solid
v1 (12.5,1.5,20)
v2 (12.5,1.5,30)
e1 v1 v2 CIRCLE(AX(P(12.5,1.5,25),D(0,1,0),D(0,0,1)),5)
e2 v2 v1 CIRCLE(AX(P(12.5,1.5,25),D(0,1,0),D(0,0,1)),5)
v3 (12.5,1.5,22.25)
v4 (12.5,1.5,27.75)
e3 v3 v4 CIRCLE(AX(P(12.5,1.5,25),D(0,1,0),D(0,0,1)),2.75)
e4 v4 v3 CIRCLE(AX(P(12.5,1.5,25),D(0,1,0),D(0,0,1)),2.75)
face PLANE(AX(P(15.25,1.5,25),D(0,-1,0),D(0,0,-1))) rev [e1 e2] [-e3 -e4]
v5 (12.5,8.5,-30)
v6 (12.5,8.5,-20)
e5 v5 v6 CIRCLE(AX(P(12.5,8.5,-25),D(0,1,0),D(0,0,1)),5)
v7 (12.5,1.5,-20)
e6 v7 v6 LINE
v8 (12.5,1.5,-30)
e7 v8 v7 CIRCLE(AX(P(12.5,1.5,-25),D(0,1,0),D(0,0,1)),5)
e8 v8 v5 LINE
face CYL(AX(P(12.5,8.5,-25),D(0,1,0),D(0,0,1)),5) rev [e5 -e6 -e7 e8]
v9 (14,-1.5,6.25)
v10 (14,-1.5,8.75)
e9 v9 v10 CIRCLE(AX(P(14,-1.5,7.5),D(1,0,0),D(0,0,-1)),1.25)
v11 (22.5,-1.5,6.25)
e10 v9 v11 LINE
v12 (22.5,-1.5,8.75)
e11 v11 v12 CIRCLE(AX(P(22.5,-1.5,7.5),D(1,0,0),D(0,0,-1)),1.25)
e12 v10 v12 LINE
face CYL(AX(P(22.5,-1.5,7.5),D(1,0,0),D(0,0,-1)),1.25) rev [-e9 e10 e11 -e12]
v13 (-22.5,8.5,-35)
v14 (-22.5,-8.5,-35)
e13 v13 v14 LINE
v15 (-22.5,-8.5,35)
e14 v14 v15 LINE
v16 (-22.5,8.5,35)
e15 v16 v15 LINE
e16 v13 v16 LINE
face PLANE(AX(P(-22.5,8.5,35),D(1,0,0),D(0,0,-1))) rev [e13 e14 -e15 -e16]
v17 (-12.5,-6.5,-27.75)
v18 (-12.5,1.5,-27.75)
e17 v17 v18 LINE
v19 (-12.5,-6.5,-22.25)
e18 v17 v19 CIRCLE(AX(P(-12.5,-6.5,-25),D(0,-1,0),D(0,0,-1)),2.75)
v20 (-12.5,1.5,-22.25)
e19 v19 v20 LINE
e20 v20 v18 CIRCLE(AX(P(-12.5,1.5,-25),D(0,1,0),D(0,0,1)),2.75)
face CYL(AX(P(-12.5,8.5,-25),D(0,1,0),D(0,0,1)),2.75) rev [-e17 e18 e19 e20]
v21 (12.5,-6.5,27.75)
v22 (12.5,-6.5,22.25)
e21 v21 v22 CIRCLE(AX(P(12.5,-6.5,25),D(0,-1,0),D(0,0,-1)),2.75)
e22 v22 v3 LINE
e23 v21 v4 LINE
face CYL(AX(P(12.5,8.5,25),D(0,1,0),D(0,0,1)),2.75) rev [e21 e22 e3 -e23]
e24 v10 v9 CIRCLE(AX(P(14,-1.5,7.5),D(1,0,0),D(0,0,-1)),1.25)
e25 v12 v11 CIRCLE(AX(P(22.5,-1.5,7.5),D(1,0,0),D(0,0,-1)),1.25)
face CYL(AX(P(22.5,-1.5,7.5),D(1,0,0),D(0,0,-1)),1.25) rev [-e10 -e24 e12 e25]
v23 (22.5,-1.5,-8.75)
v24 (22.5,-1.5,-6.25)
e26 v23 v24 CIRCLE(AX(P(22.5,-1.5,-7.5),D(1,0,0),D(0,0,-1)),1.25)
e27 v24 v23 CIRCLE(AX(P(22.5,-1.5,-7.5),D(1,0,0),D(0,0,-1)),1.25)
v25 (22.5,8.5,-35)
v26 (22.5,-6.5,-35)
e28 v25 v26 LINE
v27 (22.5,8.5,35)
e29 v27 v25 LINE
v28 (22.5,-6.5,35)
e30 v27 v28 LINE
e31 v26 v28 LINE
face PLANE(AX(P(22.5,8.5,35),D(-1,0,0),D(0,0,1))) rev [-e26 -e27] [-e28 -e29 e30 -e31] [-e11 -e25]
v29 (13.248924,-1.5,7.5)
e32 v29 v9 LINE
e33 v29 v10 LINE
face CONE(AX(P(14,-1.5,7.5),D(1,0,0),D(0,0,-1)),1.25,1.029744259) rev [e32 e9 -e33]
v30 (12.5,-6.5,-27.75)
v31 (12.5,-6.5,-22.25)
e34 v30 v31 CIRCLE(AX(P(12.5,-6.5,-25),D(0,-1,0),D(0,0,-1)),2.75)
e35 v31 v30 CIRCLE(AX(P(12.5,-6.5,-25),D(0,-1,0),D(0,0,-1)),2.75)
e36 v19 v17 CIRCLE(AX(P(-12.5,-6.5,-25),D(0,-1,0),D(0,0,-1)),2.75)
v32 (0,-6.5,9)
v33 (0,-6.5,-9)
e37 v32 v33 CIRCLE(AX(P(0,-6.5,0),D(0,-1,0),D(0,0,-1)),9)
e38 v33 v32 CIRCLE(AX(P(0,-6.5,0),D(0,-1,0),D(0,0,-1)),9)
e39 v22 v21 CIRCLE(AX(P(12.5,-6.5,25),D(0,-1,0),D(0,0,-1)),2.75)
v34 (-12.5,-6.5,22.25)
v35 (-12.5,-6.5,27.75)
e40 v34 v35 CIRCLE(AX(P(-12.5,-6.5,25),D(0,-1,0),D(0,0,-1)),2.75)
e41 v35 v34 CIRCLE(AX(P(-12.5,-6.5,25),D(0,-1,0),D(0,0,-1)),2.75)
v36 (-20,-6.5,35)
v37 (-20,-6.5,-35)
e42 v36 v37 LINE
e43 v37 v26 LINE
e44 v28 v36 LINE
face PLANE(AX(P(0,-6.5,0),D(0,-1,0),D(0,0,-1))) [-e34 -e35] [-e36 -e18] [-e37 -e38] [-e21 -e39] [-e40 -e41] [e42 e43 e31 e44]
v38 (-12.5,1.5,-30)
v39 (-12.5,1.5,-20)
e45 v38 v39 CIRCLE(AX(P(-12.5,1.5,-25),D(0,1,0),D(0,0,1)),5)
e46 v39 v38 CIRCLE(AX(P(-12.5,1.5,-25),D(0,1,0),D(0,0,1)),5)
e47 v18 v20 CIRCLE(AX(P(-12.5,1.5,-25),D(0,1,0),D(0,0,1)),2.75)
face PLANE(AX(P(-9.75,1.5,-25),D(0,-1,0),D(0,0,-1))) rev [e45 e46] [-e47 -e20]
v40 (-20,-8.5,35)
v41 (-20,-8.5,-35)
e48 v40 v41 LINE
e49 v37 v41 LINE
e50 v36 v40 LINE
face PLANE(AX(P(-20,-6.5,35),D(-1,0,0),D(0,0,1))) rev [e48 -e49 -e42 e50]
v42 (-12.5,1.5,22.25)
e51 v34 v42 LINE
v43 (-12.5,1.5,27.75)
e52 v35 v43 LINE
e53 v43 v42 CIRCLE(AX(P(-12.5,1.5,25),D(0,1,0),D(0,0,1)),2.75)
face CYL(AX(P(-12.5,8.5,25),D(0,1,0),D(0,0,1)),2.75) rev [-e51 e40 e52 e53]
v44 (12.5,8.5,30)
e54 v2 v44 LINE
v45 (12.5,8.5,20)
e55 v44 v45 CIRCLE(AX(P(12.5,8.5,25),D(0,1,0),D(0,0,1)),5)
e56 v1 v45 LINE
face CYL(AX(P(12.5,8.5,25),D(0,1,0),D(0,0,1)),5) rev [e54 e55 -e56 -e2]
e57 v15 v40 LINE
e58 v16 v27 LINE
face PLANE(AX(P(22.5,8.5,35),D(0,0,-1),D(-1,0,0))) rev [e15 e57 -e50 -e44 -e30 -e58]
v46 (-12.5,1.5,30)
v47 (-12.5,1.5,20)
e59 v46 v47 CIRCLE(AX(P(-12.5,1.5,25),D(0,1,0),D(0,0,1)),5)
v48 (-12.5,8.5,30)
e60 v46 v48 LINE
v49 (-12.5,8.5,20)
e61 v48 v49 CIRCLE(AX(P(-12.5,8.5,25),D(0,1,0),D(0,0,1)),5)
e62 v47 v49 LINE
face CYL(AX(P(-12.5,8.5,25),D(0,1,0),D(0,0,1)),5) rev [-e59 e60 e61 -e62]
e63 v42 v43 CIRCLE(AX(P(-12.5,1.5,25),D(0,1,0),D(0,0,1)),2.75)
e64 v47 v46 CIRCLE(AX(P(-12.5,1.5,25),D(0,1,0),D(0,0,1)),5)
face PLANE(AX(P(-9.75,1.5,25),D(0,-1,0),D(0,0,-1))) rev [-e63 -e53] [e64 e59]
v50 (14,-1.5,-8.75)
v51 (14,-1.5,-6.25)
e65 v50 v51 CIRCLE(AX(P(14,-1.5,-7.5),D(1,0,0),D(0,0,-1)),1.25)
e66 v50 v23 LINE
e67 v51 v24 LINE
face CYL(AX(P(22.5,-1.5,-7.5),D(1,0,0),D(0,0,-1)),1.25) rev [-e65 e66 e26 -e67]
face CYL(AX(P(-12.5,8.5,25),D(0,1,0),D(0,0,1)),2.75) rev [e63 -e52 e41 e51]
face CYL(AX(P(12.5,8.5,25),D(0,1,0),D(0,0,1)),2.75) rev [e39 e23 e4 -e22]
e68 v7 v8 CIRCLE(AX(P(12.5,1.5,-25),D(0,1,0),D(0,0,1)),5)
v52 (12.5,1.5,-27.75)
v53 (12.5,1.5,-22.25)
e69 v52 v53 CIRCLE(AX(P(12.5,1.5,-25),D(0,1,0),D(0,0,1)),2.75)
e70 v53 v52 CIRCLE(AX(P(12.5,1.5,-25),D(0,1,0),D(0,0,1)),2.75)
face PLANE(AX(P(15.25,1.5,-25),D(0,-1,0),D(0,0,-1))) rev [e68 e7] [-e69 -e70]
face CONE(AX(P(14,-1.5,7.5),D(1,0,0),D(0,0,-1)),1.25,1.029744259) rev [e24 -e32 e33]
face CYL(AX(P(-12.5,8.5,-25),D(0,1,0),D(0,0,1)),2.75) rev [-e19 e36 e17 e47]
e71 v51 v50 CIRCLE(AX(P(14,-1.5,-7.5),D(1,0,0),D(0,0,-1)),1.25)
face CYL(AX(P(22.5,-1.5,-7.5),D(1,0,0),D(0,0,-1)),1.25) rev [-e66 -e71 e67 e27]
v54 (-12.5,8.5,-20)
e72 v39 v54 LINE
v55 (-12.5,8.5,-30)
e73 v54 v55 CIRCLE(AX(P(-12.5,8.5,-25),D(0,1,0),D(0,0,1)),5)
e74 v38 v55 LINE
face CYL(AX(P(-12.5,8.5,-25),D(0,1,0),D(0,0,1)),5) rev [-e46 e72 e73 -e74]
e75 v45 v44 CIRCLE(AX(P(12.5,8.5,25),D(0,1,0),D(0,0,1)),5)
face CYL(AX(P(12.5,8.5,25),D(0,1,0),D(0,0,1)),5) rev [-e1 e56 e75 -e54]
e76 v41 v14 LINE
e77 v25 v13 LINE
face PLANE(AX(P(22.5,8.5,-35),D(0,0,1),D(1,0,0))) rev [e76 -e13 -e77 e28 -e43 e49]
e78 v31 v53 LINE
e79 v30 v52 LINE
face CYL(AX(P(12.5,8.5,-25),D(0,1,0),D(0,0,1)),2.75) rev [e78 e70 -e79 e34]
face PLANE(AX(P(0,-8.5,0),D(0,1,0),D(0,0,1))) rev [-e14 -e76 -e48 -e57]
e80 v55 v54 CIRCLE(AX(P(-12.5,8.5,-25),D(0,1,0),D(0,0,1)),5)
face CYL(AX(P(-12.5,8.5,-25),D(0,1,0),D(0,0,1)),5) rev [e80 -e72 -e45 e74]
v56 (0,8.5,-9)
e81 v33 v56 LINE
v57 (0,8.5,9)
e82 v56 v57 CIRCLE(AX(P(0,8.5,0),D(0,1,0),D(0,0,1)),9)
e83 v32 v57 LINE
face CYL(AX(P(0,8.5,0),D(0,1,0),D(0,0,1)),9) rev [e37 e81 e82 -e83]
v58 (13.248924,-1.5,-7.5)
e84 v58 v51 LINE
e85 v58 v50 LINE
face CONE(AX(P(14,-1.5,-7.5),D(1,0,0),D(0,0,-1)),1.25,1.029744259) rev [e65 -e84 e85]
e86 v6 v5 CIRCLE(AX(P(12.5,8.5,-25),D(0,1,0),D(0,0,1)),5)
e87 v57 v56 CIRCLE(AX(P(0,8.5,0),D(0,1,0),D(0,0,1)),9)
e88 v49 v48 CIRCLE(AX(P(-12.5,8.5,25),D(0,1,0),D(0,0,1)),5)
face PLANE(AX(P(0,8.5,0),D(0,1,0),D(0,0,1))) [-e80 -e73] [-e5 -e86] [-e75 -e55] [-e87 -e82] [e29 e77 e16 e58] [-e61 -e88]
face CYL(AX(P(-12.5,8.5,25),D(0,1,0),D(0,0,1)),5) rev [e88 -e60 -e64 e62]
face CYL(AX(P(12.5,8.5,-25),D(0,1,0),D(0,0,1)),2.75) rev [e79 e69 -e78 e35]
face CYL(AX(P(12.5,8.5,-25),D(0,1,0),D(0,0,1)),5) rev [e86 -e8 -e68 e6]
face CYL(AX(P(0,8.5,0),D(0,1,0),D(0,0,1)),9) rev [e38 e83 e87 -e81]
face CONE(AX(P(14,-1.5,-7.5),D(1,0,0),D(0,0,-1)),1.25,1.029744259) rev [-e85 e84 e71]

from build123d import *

# Parameters (mm, degrees)
SKETCH_1_W                = 45
SKETCH_1_H                = 70
EXTRUDE_1_DEPTH           = 8.5
SKETCH_2_W                = 42.5
SKETCH_2_H                = 70
CUT_EXTRUDE_1_DEPTH       = 2
HOLE_WIZARD_1_D           = 5.5
HOLE_WIZARD_1_CBORE_D     = 10
HOLE_WIZARD_1_CBORE_DEPTH = 7
HOLE_WIZARD_18_0_18_1_D   = 18
HOLE_WIZARD_M3_1_D        = 2.5
HOLE_WIZARD_M3_1_DEPTH    = 8.5
HOLE_WIZARD_M3_1_TIP      = 0.751075774


with BuildPart() as part:
    # 草图1 → 凸台-拉伸1 (new, symmetric)
    with BuildSketch(Plane(origin=(0, 0, 0), x_dir=(1, 0, 0), z_dir=(0, 1, 0))):
        Rectangle(SKETCH_1_W, SKETCH_1_H)
    extrude(amount=EXTRUDE_1_DEPTH, both=True)

    # 草图2 → 切除-拉伸1 (cut)
    with BuildSketch(Plane.XZ.offset(8.5)):
        with Locations((1.25, 0)):
            Rectangle(SKETCH_2_W, SKETCH_2_H)
    extrude(amount=-CUT_EXTRUDE_1_DEPTH, mode=Mode.SUBTRACT)

    # 打孔尺寸(%根据)内六角圆柱头螺钉的类型1 (through all)
    with Locations(Plane(origin=(0, 8.5, 0), x_dir=(1, 0, 0), z_dir=(0, 1, 0))):
        with Locations((-12.5, -25), (-12.5, 25), (12.5, 25), (12.5, -25)):
            CounterBoreHole(HOLE_WIZARD_1_D / 2, HOLE_WIZARD_1_CBORE_D / 2, HOLE_WIZARD_1_CBORE_DEPTH)

    # Ø18.0 (18) 直径孔1 (through all)
    with Locations(Plane(origin=(0, 8.5, 0), x_dir=(1, 0, 0), z_dir=(0, 1, 0))):
        with Locations((0, 0)):
            Hole(HOLE_WIZARD_18_0_18_1_D / 2)

    # M3 螺纹孔1
    with Locations(Plane(origin=(22.5, 0, 0), x_dir=(0, 0, -1), z_dir=(1, 0, 0))):
        with Locations((7.5, -1.5), (-7.5, -1.5)):
            Hole(HOLE_WIZARD_M3_1_D / 2, depth=HOLE_WIZARD_M3_1_DEPTH)
            with Locations((0, 0, -(HOLE_WIZARD_M3_1_DEPTH + HOLE_WIZARD_M3_1_TIP / 2))):  # 118° drill point
                Cone(0, HOLE_WIZARD_M3_1_D / 2, HOLE_WIZARD_M3_1_TIP, mode=Mode.SUBTRACT)


solid = part.part
